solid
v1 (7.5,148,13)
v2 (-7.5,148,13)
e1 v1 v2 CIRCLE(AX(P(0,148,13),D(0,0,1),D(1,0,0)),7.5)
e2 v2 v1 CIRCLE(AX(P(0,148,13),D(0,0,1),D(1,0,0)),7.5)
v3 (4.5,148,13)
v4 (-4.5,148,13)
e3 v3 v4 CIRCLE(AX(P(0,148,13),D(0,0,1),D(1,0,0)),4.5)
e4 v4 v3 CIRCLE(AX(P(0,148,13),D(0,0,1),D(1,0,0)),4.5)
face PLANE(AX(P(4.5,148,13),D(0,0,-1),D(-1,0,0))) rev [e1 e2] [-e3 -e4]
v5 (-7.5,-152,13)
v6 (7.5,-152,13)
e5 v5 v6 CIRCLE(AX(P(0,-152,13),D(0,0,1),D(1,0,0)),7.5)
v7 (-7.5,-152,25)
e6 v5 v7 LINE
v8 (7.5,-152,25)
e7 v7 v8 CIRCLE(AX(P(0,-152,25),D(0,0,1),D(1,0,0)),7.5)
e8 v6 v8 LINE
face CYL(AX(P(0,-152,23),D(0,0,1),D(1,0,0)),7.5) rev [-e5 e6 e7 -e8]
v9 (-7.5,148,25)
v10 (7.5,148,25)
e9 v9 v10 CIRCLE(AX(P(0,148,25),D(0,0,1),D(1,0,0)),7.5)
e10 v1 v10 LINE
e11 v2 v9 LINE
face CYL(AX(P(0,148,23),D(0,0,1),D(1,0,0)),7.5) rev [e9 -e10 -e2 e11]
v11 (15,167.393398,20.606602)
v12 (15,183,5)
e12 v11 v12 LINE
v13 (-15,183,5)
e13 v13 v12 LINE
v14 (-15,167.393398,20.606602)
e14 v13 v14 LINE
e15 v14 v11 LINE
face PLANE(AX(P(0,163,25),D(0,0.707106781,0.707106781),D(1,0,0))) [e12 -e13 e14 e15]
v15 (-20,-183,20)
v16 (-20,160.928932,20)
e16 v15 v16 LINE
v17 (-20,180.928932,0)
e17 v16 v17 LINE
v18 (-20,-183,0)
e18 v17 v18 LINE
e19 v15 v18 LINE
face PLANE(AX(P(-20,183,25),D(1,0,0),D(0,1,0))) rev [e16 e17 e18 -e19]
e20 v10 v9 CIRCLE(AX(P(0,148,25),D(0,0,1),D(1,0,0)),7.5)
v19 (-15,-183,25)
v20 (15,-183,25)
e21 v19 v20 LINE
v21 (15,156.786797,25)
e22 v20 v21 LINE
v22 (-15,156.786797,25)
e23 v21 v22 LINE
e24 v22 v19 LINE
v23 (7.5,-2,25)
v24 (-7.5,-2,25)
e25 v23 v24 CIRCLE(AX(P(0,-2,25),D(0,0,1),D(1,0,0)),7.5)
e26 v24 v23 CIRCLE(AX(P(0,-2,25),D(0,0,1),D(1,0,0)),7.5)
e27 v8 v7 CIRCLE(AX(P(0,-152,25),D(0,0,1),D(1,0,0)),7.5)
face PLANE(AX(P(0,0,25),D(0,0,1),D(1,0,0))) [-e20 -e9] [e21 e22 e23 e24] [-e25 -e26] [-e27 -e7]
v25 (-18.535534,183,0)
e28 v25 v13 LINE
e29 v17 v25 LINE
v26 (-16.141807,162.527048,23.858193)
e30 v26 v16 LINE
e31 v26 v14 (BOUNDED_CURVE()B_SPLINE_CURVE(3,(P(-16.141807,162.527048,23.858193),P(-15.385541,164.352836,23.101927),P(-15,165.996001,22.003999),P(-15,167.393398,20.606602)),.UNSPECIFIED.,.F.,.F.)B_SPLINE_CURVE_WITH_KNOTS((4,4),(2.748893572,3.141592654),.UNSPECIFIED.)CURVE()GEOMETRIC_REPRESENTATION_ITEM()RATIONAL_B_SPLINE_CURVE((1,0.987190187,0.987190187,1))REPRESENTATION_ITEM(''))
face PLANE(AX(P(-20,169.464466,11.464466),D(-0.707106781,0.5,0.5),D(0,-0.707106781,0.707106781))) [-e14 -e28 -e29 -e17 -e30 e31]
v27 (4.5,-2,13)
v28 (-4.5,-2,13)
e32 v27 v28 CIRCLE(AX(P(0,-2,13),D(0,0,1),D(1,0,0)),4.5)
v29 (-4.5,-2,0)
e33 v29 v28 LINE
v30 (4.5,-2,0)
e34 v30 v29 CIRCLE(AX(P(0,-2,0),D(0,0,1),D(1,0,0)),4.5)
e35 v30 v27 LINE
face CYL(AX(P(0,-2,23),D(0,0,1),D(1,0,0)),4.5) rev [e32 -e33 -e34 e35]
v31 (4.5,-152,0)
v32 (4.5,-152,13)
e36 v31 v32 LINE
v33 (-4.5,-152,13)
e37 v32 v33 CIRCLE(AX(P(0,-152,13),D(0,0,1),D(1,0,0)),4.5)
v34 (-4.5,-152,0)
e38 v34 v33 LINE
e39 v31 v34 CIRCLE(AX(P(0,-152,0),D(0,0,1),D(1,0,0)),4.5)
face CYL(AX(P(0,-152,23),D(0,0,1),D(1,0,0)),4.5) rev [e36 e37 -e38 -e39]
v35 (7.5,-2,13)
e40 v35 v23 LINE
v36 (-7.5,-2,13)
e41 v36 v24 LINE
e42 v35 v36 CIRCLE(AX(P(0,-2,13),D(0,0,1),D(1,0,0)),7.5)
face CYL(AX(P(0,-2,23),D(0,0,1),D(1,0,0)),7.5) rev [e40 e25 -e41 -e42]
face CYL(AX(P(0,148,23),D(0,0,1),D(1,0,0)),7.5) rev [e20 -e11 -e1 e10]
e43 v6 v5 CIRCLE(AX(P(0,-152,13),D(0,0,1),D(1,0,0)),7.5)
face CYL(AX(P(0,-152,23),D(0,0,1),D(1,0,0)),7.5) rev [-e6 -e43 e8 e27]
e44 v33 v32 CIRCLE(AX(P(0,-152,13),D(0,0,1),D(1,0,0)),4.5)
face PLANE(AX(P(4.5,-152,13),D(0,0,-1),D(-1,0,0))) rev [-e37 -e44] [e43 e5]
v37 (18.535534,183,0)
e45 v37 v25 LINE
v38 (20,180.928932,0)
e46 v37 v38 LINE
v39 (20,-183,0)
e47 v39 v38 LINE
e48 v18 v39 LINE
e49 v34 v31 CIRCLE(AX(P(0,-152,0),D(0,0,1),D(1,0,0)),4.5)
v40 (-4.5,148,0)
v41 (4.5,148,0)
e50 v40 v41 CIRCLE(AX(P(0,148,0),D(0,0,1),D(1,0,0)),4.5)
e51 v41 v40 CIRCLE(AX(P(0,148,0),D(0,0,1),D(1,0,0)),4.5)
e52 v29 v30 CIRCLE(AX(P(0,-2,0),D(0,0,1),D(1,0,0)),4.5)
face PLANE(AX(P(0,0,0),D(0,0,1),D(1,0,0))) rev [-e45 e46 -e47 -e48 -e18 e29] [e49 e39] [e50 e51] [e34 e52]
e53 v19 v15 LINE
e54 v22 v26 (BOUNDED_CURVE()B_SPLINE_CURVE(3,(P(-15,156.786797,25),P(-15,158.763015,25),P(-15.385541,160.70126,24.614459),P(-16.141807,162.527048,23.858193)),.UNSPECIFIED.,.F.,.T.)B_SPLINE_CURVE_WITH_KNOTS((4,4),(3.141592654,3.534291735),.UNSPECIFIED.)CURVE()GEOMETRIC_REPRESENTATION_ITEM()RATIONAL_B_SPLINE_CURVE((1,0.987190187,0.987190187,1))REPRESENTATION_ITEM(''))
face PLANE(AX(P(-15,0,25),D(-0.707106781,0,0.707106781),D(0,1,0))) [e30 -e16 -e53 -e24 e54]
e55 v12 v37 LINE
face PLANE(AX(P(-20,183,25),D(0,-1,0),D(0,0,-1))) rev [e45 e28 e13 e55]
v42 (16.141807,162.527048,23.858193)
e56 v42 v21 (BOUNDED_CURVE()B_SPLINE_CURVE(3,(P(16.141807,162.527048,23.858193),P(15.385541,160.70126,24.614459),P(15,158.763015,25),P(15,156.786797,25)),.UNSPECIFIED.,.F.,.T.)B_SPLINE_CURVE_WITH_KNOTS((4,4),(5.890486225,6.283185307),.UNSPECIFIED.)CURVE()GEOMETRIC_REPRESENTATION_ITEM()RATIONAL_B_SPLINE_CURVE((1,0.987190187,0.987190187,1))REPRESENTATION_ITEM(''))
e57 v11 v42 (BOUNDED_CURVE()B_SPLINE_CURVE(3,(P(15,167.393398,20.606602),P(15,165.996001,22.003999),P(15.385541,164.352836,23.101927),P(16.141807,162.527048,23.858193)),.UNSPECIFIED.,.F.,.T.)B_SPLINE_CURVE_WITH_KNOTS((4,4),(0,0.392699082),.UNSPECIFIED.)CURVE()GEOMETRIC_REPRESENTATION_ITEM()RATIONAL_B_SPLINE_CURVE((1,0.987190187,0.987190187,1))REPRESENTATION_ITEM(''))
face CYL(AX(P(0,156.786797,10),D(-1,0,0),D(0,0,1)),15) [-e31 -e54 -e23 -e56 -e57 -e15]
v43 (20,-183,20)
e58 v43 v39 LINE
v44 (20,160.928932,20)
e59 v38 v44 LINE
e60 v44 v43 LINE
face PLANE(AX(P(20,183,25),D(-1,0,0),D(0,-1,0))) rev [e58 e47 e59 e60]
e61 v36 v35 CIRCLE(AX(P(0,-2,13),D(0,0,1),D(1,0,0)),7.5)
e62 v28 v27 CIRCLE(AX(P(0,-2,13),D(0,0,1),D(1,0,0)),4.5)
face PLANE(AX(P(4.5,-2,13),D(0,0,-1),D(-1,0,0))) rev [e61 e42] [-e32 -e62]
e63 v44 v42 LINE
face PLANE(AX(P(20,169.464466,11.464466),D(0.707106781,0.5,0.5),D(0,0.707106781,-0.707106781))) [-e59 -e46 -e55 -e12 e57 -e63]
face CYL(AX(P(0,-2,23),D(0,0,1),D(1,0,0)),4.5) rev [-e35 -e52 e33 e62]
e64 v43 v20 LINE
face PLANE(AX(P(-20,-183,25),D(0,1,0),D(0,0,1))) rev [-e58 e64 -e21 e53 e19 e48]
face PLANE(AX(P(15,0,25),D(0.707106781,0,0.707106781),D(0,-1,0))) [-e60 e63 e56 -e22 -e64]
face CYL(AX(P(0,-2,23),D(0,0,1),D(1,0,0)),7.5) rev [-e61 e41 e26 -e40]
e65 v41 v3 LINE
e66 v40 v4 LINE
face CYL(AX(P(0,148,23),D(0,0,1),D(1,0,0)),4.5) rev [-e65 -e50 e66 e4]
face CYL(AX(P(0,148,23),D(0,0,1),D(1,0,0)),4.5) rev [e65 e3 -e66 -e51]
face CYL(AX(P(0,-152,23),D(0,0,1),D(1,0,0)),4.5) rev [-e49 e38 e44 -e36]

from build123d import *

# Parameters (mm, degrees)
SKETCH1_W                                          = 40
SKETCH1_H                                          = 366
BOSS_EXTRUDE1_DEPTH                                = 25
CHAMFER2_SIZE                                      = 20
SKETCH4_R                                          = 7.5
CUT_EXTRUDE1_DEPTH                                 = 2
HOLE_SIZE_BASED_ON_HEX_SOCKET_CAP_SCRE_D           = 9
HOLE_SIZE_BASED_ON_HEX_SOCKET_CAP_SCRE_CBORE_D     = 15
HOLE_SIZE_BASED_ON_HEX_SOCKET_CAP_SCRE_CBORE_DEPTH = 10
CHAMFER3_SIZE                                      = 5
CHAMFER4_SIZE                                      = 5
FILLET4_R                                          = 15


with BuildPart() as part:
    # Sketch1 → Boss-Extrude1 (new body)
    with BuildSketch(Plane.XY):
        Rectangle(SKETCH1_W, SKETCH1_H)
    extrude(amount=BOSS_EXTRUDE1_DEPTH)

    # Chamfer2
    chamfer2_edges = [part.edges().sort_by_distance(p)[0] for p in [
        (0, 183, 25),
    ]]
    chamfer(chamfer2_edges, length=CHAMFER2_SIZE)

    # Sketch4 → Cut-Extrude1 (cut)
    with BuildSketch(Plane.XY.offset(25)):
        with Locations((0, -152)):
            Circle(SKETCH4_R)
        with Locations((0, -2)):
            Circle(SKETCH4_R)
        with Locations((0, 148)):
            Circle(SKETCH4_R)
    extrude(amount=-CUT_EXTRUDE1_DEPTH, mode=Mode.SUBTRACT)

    # Hole Size (based on) hex socket cap screw type 1 (through all)
    with Locations(Plane.XY.offset(23)):
        with Locations((0, -152), (0, -2), (0, 148)):
            CounterBoreHole(HOLE_SIZE_BASED_ON_HEX_SOCKET_CAP_SCRE_D / 2, HOLE_SIZE_BASED_ON_HEX_SOCKET_CAP_SCRE_CBORE_D / 2, HOLE_SIZE_BASED_ON_HEX_SOCKET_CAP_SCRE_CBORE_DEPTH)

    # Chamfer3
    chamfer3_edges = [part.edges().sort_by_distance(p)[0] for p in [
        (-20, -10, 25),
        (20, -10, 25),
    ]]
    chamfer(chamfer3_edges, length=CHAMFER3_SIZE)

    # Chamfer4
    chamfer4_edges = [part.edges().sort_by_distance(p)[0] for p in [
        (20, 175.5, 12.5),
        (-20, 175.5, 12.5),
    ]]
    chamfer(chamfer4_edges, length=CHAMFER4_SIZE)

    # Fillet4
    fillet4_edges = [part.edges().sort_by_distance(p)[0] for p in [
        (0, 163, 25),
    ]]
    fillet(fillet4_edges, radius=FILLET4_R)


solid = part.part
